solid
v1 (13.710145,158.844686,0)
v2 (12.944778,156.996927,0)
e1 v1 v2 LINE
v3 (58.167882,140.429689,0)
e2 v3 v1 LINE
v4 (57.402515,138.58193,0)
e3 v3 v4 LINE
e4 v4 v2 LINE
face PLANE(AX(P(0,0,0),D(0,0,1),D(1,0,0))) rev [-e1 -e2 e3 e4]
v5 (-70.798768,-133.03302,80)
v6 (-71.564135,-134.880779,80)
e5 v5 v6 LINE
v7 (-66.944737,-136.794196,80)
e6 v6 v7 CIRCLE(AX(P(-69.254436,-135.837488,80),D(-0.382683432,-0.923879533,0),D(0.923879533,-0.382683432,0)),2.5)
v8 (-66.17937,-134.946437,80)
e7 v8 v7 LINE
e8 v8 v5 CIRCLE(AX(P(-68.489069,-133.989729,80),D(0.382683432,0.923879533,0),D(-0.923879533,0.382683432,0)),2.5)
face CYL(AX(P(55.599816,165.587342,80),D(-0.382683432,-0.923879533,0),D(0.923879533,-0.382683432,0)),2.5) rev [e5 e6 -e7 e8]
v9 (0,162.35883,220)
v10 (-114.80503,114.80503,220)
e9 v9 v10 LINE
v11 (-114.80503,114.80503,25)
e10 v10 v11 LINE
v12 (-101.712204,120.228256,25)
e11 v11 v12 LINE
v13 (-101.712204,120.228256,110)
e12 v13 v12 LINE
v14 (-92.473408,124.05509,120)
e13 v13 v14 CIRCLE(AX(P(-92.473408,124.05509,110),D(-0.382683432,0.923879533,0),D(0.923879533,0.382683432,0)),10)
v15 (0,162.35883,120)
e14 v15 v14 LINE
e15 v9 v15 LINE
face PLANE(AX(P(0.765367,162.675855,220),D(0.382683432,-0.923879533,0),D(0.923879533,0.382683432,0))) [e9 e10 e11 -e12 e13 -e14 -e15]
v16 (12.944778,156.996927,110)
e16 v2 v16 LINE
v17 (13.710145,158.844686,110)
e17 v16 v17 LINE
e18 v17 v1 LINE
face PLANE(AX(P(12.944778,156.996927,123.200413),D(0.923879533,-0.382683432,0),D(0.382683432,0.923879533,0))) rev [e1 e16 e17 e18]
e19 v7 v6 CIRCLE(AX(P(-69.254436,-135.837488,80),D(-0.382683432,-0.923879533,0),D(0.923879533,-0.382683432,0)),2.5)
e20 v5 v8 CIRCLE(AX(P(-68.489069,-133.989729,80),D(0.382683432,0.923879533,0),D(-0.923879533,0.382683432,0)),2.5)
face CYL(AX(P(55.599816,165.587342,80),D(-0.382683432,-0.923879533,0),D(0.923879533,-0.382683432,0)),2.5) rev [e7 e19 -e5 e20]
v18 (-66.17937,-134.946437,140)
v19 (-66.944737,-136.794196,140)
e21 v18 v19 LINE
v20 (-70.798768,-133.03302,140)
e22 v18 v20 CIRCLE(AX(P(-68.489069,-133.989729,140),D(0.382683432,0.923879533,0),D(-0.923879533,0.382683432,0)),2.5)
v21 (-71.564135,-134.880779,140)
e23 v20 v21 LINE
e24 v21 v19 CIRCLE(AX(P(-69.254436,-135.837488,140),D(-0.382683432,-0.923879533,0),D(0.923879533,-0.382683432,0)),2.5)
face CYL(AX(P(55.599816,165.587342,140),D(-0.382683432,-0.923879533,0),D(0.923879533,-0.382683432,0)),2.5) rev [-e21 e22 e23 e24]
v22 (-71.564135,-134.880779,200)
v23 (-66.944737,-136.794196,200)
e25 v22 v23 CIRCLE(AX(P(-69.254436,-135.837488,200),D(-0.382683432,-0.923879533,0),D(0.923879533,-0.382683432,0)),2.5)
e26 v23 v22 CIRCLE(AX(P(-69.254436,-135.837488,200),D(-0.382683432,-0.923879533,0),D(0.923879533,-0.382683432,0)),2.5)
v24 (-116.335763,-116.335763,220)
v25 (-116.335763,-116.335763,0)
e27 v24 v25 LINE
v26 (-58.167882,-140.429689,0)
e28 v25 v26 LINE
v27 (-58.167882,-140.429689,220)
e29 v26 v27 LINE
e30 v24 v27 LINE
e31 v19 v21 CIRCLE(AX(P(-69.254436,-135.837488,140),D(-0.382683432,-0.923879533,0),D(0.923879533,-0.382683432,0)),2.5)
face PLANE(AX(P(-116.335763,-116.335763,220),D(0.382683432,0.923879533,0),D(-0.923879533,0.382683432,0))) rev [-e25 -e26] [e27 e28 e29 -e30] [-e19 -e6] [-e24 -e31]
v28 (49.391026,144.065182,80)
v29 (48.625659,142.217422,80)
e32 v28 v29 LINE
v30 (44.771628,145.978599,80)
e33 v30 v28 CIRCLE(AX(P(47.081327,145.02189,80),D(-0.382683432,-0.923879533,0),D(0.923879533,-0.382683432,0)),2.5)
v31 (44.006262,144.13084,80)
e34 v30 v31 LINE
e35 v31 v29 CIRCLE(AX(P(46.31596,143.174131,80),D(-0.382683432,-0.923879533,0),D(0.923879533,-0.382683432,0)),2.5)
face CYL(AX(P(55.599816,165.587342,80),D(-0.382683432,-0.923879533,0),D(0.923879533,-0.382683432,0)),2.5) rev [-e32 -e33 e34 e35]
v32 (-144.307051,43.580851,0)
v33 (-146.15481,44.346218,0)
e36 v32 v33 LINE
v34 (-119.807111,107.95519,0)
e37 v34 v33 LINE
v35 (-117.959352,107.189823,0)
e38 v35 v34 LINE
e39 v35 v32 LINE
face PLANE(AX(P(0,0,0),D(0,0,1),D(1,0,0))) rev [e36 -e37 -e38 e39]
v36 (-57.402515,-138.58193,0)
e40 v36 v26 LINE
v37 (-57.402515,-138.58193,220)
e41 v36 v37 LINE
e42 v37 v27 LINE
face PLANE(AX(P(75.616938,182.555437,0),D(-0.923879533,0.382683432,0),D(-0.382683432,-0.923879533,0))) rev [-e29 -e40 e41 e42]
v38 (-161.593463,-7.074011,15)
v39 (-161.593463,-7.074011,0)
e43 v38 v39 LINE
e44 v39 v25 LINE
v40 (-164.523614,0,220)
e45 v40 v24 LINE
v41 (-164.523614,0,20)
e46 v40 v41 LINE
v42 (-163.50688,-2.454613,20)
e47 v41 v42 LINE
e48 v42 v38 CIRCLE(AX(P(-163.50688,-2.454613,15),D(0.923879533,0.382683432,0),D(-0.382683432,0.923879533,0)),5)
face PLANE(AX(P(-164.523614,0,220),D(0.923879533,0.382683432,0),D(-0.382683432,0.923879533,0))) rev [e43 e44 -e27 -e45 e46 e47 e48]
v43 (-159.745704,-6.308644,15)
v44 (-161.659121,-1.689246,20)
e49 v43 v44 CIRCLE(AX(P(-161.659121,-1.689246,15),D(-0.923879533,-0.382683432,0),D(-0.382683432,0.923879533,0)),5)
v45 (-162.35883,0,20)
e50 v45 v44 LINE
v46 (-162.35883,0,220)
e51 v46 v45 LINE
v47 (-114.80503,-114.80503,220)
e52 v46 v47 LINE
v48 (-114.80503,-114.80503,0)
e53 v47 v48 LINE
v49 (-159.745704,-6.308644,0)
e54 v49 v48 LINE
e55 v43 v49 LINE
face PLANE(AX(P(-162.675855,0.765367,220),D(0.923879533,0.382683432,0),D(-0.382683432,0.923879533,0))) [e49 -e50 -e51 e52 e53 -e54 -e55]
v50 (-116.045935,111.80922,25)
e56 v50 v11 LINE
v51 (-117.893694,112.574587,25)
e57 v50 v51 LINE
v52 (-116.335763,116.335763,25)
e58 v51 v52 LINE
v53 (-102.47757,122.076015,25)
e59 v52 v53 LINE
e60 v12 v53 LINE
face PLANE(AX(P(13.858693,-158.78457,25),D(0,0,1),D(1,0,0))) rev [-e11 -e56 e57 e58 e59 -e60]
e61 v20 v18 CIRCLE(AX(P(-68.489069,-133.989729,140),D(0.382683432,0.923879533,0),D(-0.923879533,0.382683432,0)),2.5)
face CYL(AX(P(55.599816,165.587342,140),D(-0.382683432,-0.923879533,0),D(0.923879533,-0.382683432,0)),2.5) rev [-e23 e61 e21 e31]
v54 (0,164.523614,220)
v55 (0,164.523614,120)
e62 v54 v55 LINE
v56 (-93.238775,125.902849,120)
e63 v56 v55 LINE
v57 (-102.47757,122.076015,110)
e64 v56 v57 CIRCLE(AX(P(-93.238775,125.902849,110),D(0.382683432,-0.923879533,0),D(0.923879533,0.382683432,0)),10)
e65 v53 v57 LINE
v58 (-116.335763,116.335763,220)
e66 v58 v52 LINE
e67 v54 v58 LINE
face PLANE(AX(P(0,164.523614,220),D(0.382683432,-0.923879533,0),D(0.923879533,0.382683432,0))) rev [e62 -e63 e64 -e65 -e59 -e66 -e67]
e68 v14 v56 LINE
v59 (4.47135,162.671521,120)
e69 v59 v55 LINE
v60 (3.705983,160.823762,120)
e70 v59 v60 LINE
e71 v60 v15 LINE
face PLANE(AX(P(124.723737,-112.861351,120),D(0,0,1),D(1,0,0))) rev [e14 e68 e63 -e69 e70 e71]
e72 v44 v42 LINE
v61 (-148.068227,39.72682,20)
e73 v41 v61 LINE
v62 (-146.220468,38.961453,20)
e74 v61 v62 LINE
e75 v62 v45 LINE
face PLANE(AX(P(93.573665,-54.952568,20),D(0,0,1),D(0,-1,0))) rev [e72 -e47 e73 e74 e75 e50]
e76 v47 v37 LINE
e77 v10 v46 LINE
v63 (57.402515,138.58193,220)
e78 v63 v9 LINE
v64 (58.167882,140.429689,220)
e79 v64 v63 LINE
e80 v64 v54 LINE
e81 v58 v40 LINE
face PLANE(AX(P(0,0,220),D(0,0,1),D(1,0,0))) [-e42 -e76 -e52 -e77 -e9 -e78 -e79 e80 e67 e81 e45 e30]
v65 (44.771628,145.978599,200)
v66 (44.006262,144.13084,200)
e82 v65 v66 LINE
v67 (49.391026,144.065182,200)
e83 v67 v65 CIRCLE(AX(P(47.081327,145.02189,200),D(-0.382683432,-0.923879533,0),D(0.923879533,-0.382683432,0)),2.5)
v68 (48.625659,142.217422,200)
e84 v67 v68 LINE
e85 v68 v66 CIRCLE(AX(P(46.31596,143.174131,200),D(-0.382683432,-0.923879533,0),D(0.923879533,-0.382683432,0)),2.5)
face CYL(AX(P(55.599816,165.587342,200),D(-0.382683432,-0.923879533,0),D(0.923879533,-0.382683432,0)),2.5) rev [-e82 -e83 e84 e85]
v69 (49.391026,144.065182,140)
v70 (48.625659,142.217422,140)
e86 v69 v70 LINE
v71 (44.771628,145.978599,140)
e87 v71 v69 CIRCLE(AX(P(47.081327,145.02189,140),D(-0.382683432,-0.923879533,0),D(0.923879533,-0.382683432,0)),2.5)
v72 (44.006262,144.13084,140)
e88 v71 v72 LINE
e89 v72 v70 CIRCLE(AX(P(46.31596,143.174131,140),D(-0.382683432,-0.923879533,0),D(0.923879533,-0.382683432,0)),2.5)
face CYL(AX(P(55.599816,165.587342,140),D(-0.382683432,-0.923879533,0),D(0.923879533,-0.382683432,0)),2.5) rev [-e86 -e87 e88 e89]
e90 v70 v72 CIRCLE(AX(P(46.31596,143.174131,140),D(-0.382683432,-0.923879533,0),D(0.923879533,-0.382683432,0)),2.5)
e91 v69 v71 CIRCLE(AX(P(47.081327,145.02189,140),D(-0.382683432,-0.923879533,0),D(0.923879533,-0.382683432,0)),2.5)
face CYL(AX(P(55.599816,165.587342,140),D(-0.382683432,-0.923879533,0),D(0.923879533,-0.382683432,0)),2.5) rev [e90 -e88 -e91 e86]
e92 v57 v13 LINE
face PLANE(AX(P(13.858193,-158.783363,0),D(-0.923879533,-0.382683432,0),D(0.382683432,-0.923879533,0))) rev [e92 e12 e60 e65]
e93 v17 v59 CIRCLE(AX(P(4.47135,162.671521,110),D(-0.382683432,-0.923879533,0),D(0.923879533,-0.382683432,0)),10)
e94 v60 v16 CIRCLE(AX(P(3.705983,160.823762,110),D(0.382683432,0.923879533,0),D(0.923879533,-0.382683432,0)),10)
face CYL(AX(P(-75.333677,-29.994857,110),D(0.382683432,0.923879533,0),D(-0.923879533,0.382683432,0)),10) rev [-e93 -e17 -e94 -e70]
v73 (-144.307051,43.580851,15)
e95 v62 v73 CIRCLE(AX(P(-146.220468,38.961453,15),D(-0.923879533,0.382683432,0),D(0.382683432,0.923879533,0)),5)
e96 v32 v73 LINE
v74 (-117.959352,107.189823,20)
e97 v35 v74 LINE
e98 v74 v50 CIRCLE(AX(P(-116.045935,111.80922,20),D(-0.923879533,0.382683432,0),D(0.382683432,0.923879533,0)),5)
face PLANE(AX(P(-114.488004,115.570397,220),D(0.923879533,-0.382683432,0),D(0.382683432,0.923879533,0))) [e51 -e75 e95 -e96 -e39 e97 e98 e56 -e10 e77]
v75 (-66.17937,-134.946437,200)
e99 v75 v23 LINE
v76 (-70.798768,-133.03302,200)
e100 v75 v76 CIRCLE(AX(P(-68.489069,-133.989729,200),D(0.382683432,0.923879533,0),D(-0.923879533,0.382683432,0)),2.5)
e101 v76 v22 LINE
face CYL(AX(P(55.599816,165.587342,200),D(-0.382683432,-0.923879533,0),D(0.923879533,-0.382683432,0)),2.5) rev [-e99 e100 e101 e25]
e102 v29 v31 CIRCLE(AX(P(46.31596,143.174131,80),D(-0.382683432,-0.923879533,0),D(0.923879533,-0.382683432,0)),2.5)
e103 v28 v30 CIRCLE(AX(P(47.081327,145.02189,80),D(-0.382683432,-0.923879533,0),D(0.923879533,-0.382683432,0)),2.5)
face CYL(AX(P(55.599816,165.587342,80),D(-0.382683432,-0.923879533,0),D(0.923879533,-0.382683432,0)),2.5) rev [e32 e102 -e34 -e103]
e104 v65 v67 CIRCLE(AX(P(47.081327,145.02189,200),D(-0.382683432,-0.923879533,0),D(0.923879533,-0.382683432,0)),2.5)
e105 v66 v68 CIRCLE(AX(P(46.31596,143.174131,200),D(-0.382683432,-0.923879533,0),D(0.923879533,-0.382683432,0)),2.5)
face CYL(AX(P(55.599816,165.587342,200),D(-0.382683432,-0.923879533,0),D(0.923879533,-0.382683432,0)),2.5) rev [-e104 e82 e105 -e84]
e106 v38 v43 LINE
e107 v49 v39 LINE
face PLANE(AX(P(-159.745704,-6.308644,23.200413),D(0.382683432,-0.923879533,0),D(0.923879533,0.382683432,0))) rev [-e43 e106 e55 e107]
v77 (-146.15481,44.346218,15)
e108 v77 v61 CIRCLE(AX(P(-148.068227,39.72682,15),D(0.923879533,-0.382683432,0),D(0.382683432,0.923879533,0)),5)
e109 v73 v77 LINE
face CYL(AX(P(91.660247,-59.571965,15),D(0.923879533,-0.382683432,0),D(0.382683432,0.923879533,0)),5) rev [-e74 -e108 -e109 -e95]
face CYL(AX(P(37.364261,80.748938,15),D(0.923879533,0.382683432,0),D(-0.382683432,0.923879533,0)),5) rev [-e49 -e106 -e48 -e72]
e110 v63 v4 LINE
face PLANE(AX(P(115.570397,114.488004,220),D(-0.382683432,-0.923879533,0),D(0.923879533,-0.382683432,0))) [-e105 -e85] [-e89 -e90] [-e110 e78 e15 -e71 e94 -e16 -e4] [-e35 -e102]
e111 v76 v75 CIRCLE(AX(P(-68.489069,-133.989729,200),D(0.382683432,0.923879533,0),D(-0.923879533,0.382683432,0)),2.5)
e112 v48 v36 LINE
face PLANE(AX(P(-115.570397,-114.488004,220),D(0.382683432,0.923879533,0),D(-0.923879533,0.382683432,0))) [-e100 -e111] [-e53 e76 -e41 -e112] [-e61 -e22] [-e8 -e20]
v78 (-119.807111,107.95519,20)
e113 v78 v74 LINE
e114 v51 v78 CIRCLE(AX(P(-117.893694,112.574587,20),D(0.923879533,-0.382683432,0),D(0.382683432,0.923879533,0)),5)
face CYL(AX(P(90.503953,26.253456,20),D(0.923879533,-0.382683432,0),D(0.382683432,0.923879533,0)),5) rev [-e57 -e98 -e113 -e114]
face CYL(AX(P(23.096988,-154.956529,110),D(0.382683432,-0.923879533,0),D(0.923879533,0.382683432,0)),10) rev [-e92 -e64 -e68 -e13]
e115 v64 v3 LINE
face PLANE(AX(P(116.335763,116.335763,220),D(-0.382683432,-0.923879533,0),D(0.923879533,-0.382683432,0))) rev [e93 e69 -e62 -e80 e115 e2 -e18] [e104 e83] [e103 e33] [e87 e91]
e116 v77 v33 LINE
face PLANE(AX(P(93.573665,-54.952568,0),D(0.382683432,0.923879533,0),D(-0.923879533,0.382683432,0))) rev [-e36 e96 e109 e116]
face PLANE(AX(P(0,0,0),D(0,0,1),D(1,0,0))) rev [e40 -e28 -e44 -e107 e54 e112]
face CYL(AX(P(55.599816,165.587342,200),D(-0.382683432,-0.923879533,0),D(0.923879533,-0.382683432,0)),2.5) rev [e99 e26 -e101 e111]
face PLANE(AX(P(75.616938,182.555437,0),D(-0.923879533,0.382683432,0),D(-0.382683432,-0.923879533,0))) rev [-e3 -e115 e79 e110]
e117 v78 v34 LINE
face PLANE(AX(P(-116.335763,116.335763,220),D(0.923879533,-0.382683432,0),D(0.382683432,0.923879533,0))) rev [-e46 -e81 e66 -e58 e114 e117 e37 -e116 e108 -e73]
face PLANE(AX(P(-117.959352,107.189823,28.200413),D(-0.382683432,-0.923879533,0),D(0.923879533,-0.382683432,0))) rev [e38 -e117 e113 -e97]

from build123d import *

# Parameters (mm, degrees)
BOSS_EXTRUDE1_DEPTH = 220
SHELL1_T            = -2
CUT_EXTRUDE1_DEPTH  = 321.212491043
SKETCH3_R           = 2.5
CUT_EXTRUDE2_DEPTH  = 394.612153142
SKETCH4_W           = 120
SKETCH4_H           = 120
CUT_EXTRUDE3_DEPTH  = 376.254580252
CUT_EXTRUDE4_DEPTH  = 120
FILLET1_R           = 10
CUT_EXTRUDE5_REACH  = 377.255
SKETCH6_W           = 20
SKETCH6_H           = 25
CUT_EXTRUDE6_DEPTH  = 25
FILLET2_R           = 5
SKETCH8_W           = 20
SKETCH8_H           = 52
CUT_EXTRUDE7_DEPTH  = 357.766015962
CUT_EXTRUDE8_DEPTH  = 20
FILLET3_R           = 5


with BuildPart() as part:
    # Sketch1 → Boss-Extrude1 (new body)
    with BuildSketch(Plane.XY):
        Polygon((-164.523614444, 0), (-116.335763439, -116.335763439), (0, -164.523614444), (116.335763439, -116.335763439), (164.523614444, 0), (116.335763439, 116.335763439), (0, 164.523614444), (-116.335763439, 116.335763439), align=None)
    extrude(amount=BOSS_EXTRUDE1_DEPTH)

    # Shell1
    shell1_openings = [part.faces().sort_by_distance(p)[0] for p in [
        (0, 0, 220),
        (0, 0, 0),
    ]]
    offset(amount=SHELL1_T, openings=shell1_openings, kind=Kind.INTERSECTION)

    # Sketch2 → Cut-Extrude1 (cut, through all)
    with BuildSketch(Plane.XY.offset(220)):
        Polygon((75.61693775, 182.555436661), (-82.042454152, -198.068005503), (95.714298716, -271.697263345), (253.373690618, 108.92617882), align=None)
    extrude(amount=-CUT_EXTRUDE1_DEPTH, mode=Mode.SUBTRACT)

    # Sketch3 → Cut-Extrude2 (cut, through all)
    with BuildSketch(Plane(origin=(-58.167881719, -140.429688942, 0), x_dir=(0.9238795325112961, -0.3826834323650676, 0), z_dir=(-0.3826834323650675, -0.923879532511296, 0))):
        with Locations((-12, 200)):
            Circle(SKETCH3_R)
        with Locations((-12, 140)):
            Circle(SKETCH3_R)
        with Locations((-12, 80)):
            Circle(SKETCH3_R)
    extrude(amount=-CUT_EXTRUDE2_DEPTH, mode=Mode.SUBTRACT)

    # Sketch4 → Cut-Extrude3 (cut, through all)
    with BuildSketch(Plane(origin=(-58.167881719, 140.429688942, 0), x_dir=(0.9238795325112777, 0.3826834323651116, 0), z_dir=(-0.38268343236511165, 0.9238795325112779, 0))):
        with Locations((12.039538519, -60)):
            Rectangle(SKETCH4_W, SKETCH4_H)
    extrude(amount=-CUT_EXTRUDE3_DEPTH, mode=Mode.SUBTRACT)

    # Sketch5 → Cut-Extrude4 (cut)
    with BuildSketch(Plane(origin=(0, 0, 0), x_dir=(-1, 0, 0), z_dir=(0, 0, -1))):
        Polygon((-12.944778014, 156.996927428), (-11.862385814, 159.610053358), (-13.710144879, 158.844686494), align=None)
    extrude(amount=-CUT_EXTRUDE4_DEPTH, mode=Mode.SUBTRACT)

    # Fillet1
    fillet1_edges = [part.edges().sort_by_distance(p)[0] for p in [
        (-102.094887019, 121.152135392, 120),
        (13.327461447, 157.920806961, 120),
    ]]
    fillet(fillet1_edges, radius=FILLET1_R)

    # Sketch6 → Cut-Extrude5 (cut, up to next)
    with BuildSketch(Plane(origin=(-58.167881719, 140.429688942, 0), x_dir=(0.9238795325112777, 0.3826834323651116, 0), z_dir=(-0.38268343236511165, 0.9238795325112779, 0)), mode=Mode.PRIVATE) as cut_extrude5_sk1:
        with Locations((-57.960461481, -12.5)):
            Rectangle(SKETCH6_W, SKETCH6_H)
    cut_extrude5_tool1 = extrude(cut_extrude5_sk1.sketch, amount=-CUT_EXTRUDE5_REACH, mode=Mode.PRIVATE) & part.part
    add(cut_extrude5_tool1.solids().sort_by_distance((-111.716366, 118.249181, 12.5))[0], mode=Mode.SUBTRACT)

    # Sketch7 → Cut-Extrude6 (cut)
    with BuildSketch(Plane(origin=(0, 0, 0), x_dir=(-1, 0, 0), z_dir=(0, 0, -1))):
        Polygon((117.959351739, 107.189822685), (119.04174394, 109.802948615), (119.807110804, 107.95518955), align=None)
    extrude(amount=-CUT_EXTRUDE6_DEPTH, mode=Mode.SUBTRACT)

    # Fillet2
    fillet2_edges = [part.edges().sort_by_distance(p)[0] for p in [
        (-118.883231272, 107.572506117, 25),
    ]]
    fillet(fillet2_edges, radius=FILLET2_R)

    # Sketch8 → Cut-Extrude7 (cut, through all)
    with BuildSketch(Plane(origin=(-140.429688942, 58.167881719, 0), x_dir=(0, 0, 1), z_dir=(-0.9238795325112957, 0.3826834323650681, 0))):
        with Locations((10, -40.960461481)):
            Rectangle(SKETCH8_W, SKETCH8_H)
    extrude(amount=-CUT_EXTRUDE7_DEPTH, mode=Mode.SUBTRACT)

    # Sketch9 → Cut-Extrude8 (cut)
    with BuildSketch(Plane(origin=(0, 0, 0), x_dir=(-1, 0, 0), z_dir=(0, 0, -1))):
        Polygon((159.745704114, -6.30864406), (161.593463179, -7.074010925), (162.358830044, -5.22625186), align=None)
    extrude(amount=-CUT_EXTRUDE8_DEPTH, mode=Mode.SUBTRACT)

    # Fillet3
    fillet3_edges = [part.edges().sort_by_distance(p)[0] for p in [
        (-145.230930158, 43.963534128, 20),
        (-160.669583647, -6.691327492, 20),
    ]]
    fillet(fillet3_edges, radius=FILLET3_R)


solid = part.part
